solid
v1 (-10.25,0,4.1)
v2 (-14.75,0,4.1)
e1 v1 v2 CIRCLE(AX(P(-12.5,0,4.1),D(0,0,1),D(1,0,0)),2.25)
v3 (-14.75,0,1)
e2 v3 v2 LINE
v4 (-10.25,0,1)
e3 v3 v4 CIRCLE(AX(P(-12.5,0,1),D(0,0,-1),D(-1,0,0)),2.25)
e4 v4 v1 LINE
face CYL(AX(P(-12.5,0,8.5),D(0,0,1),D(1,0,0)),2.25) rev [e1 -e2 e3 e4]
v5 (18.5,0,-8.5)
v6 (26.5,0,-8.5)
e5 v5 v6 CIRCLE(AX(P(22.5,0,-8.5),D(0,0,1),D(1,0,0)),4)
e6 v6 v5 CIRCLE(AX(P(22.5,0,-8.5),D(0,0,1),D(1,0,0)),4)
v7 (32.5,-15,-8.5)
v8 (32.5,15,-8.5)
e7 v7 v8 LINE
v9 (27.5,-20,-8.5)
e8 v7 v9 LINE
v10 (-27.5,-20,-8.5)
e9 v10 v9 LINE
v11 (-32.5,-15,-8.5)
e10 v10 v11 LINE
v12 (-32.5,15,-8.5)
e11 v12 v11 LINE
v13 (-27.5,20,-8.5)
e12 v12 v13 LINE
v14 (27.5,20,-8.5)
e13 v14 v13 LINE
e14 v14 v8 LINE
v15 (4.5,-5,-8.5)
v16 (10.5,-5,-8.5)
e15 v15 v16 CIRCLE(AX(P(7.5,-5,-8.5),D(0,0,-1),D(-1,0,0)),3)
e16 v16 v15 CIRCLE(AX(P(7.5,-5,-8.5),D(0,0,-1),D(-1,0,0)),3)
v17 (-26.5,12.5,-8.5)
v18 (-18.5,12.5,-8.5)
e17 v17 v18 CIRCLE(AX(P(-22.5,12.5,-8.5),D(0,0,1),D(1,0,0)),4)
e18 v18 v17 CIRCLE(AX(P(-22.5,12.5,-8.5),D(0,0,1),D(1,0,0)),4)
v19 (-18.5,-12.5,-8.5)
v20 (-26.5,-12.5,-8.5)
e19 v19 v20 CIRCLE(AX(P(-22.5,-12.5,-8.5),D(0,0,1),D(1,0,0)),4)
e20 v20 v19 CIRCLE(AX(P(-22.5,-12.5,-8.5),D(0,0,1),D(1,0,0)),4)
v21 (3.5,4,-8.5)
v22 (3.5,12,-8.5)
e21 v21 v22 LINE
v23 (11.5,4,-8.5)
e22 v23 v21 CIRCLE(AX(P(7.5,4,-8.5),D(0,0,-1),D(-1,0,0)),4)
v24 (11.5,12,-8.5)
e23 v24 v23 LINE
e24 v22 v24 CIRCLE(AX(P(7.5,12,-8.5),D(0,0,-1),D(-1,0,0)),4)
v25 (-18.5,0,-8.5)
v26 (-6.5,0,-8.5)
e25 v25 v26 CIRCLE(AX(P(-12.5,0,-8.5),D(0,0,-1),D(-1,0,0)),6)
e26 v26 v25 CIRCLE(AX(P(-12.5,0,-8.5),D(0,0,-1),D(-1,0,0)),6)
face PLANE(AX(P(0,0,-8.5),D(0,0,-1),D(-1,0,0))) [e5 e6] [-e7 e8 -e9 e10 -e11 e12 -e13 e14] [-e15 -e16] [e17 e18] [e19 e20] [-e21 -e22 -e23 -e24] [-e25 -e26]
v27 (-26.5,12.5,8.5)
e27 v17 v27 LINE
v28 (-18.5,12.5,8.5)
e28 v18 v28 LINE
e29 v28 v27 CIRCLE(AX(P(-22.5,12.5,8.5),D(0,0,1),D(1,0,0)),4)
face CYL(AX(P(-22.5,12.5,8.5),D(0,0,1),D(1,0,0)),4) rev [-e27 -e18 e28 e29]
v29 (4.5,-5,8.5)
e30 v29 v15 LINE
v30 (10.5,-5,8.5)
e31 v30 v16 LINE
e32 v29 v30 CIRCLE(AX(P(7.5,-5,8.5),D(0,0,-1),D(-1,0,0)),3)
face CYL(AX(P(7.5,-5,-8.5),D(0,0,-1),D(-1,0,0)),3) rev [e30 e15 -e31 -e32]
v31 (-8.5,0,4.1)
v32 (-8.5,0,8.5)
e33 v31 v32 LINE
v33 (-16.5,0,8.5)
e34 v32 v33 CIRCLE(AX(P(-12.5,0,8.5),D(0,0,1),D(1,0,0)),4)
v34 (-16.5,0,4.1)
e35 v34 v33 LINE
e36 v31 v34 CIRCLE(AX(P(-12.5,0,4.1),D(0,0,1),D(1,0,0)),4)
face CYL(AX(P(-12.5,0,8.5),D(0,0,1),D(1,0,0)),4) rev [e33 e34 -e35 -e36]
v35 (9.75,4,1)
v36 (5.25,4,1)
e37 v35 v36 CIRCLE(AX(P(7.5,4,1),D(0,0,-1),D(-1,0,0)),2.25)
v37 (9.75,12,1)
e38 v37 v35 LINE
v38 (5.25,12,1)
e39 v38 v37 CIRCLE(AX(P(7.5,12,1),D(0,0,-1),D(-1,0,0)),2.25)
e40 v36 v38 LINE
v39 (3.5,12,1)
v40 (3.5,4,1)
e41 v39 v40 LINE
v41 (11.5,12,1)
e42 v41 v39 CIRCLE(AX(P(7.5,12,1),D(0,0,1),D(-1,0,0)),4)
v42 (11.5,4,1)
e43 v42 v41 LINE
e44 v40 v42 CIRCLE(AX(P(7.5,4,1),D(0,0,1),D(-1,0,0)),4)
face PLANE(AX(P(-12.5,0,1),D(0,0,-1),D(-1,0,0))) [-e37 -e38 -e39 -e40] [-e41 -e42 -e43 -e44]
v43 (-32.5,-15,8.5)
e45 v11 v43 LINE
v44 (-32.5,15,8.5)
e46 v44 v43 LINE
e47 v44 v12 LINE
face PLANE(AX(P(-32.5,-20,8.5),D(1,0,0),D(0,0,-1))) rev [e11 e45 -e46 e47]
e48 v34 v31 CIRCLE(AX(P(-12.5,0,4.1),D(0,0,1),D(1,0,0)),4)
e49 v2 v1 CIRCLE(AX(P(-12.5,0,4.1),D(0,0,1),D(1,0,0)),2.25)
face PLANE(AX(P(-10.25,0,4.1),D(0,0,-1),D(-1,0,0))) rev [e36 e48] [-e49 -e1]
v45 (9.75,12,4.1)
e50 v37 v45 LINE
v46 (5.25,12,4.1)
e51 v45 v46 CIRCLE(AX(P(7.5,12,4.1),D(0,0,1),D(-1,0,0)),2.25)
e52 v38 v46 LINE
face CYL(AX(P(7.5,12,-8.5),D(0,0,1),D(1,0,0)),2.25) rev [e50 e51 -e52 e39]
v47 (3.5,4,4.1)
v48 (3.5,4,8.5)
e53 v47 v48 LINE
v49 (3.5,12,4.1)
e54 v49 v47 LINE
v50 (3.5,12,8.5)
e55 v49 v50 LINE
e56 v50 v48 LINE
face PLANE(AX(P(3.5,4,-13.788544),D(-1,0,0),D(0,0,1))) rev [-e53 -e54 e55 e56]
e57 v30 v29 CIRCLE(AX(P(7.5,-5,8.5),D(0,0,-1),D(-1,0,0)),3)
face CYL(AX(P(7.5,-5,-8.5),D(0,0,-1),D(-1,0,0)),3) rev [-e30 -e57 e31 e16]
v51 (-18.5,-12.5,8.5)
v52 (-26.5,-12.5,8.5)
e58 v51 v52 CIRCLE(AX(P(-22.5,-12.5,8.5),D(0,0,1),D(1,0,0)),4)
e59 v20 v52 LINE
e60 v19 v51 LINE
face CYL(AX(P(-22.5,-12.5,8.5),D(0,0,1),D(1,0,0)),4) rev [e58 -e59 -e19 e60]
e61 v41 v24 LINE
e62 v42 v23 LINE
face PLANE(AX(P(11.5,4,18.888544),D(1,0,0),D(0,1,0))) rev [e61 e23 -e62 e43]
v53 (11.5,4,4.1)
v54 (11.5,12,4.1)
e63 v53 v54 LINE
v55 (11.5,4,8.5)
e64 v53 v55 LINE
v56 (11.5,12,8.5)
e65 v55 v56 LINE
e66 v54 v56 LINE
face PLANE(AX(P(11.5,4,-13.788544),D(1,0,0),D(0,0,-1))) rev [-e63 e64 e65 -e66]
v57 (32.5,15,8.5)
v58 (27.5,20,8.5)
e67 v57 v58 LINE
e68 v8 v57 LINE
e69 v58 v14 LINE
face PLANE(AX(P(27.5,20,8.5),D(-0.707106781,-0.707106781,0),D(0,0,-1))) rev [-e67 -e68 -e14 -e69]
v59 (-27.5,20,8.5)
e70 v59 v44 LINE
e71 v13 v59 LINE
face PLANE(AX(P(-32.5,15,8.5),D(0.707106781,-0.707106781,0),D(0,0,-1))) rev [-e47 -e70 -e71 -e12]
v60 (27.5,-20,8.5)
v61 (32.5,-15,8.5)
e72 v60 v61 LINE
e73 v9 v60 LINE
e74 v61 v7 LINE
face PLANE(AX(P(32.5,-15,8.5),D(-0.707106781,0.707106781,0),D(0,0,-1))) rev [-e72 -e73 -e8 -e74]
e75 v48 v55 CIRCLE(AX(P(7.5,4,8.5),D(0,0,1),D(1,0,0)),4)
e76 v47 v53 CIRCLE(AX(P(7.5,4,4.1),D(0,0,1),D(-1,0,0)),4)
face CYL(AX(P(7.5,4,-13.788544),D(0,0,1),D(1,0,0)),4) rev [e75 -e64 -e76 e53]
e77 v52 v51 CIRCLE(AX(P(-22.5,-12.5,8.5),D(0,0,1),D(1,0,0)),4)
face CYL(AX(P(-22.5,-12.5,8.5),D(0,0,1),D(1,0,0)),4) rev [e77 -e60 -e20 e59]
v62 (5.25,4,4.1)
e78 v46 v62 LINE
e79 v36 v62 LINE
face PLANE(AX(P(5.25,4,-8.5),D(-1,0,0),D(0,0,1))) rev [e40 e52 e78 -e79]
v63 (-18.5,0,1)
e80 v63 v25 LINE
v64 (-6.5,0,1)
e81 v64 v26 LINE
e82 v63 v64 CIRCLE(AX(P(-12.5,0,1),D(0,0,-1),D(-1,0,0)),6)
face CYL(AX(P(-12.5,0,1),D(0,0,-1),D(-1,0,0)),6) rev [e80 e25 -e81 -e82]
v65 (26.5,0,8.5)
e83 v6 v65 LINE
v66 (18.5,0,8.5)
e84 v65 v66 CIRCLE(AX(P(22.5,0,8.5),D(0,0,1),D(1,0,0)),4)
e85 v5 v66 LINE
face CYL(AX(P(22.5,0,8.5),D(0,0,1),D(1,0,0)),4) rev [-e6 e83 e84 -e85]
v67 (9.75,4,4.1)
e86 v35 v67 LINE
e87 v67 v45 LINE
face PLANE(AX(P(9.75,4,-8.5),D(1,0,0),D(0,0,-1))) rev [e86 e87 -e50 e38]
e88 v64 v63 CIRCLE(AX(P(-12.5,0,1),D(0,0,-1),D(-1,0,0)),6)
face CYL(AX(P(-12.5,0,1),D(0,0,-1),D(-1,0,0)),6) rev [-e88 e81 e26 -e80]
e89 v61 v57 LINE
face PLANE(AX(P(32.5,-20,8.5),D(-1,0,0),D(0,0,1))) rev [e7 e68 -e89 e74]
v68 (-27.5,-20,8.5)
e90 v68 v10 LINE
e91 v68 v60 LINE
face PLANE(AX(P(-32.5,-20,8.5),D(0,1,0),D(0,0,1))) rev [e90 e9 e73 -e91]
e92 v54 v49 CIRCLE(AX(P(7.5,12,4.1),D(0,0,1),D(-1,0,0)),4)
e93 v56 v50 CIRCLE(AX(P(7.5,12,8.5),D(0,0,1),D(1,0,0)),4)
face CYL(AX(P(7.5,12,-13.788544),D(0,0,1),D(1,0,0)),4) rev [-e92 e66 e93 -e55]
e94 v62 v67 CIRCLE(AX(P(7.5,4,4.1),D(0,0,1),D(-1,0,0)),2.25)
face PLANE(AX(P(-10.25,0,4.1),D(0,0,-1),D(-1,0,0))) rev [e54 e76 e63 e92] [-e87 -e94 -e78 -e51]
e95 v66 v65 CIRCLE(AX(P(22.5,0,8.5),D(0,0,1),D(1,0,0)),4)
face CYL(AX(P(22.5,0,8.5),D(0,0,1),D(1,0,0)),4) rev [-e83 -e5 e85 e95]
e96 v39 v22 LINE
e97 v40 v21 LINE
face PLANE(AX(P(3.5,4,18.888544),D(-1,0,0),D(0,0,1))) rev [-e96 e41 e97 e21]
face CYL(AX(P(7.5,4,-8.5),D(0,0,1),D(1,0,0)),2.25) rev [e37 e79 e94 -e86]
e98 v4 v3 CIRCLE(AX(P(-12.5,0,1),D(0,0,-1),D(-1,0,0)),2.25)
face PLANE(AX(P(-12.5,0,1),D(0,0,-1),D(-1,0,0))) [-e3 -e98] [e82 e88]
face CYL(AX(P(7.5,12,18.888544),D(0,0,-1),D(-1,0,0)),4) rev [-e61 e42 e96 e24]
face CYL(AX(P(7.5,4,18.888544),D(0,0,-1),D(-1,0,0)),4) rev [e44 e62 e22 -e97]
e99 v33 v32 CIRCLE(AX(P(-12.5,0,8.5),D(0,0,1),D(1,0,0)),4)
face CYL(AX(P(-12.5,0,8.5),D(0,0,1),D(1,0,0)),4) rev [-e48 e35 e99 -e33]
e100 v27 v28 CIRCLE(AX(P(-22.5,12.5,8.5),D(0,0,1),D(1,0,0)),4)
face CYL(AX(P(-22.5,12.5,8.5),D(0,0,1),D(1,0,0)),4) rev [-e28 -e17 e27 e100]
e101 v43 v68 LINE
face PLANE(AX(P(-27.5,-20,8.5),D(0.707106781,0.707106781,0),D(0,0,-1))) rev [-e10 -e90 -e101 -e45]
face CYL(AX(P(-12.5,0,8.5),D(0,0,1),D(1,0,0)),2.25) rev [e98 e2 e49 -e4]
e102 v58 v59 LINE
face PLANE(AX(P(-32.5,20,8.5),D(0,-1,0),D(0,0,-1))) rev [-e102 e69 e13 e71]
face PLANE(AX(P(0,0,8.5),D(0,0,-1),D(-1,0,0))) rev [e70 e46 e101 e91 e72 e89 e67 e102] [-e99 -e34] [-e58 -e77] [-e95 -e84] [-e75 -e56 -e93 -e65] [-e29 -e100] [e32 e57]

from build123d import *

# Parameters (mm, degrees)
SKETCH_1_W                   = 65
SKETCH_1_H                   = 40
EXTRUDE_1_DEPTH              = 8.5
HOLE_WIZARD_8_0_8_1_D        = 8
SKETCH_4_R                   = 6
CUT_EXTRUDE_1_DEPTH          = 9.5
HOLE_WIZARD_M4_1_D           = 4.5
HOLE_WIZARD_M4_1_CBORE_D     = 8
HOLE_WIZARD_M4_1_CBORE_DEPTH = 4.4
HOLE_WIZARD_6_0_6_1_D        = 6
CUT_EXTRUDE_2_DEPTH          = 9.5
CUT_EXTRUDE_3_DEPTH          = 42.776189391
CUT_EXTRUDE_START            = -4.4
CUT_EXTRUDE_4_DEPTH          = 4.4
CHAMFER_1_SIZE               = 5


with BuildPart() as part:
    # 草图1 → 凸台-拉伸1 (new, symmetric)
    with BuildSketch(Plane.XY):
        Rectangle(SKETCH_1_W, SKETCH_1_H)
    extrude(amount=EXTRUDE_1_DEPTH, both=True)

    # Ø8.0 (8) 直径孔1 (through all)
    with Locations(Plane.XY.offset(8.5)):
        with Locations((-22.5, 12.5), (-22.5, -12.5), (22.5, 0)):
            Hole(HOLE_WIZARD_8_0_8_1_D / 2)

    # 草图4 → 切除-拉伸1 (cut)
    with BuildSketch(Plane(origin=(0, 0, -8.5), x_dir=(-1, 0, 0), z_dir=(0, 0, -1))):
        with Locations((12.5, 0)):
            Circle(SKETCH_4_R)
    extrude(amount=-CUT_EXTRUDE_1_DEPTH, mode=Mode.SUBTRACT)

    # M4 六角凹头螺钉的柱形沉头孔1 (through all)
    with Locations(Plane.XY.offset(8.5)):
        with Locations((-12.5, 0)):
            CounterBoreHole(HOLE_WIZARD_M4_1_D / 2, HOLE_WIZARD_M4_1_CBORE_D / 2, HOLE_WIZARD_M4_1_CBORE_DEPTH)

    # Ø6.0 (6) 直径孔1 (through all)
    with Locations(Plane(origin=(0, 0, -8.5), x_dir=(-1, 0, 0), z_dir=(0, 0, -1))):
        with Locations((-7.5, -5)):
            Hole(HOLE_WIZARD_6_0_6_1_D / 2)

    # 草图9 → 切除-拉伸2 (cut)
    with BuildSketch(Plane(origin=(0, 0, -8.5), x_dir=(-1, 0, 0), z_dir=(0, 0, -1))):
        with BuildLine():
            Line((-11.5, 4), (-11.5, 12))
            ThreePointArc((-11.5, 12), (-7.5, 16), (-3.5, 12))
            Line((-3.5, 12), (-3.5, 4))
            ThreePointArc((-3.5, 4), (-7.5, 0), (-11.5, 4))
        make_face()
    extrude(amount=-CUT_EXTRUDE_2_DEPTH, mode=Mode.SUBTRACT)

    # 草图10 → 切除-拉伸3 (cut, through all)
    with BuildSketch(Plane.XY.offset(8.5)):
        with BuildLine():
            Line((5.25, 4), (5.25, 12))
            ThreePointArc((5.25, 12), (7.5, 14.25), (9.75, 12))
            Line((9.75, 12), (9.75, 4))
            ThreePointArc((9.75, 4), (7.5, 1.75), (5.25, 4))
        make_face()
    extrude(amount=-CUT_EXTRUDE_3_DEPTH, mode=Mode.SUBTRACT)

    # 草图11 → 切除-拉伸4 (cut)
    with BuildSketch(Plane.XY.offset(8.5).offset(CUT_EXTRUDE_START)):
        with BuildLine():
            Line((3.5, 4), (3.5, 12))
            ThreePointArc((3.5, 12), (7.5, 16), (11.5, 12))
            Line((11.5, 12), (11.5, 4))
            ThreePointArc((11.5, 4), (7.5, 0), (3.5, 4))
        make_face()
    extrude(amount=CUT_EXTRUDE_4_DEPTH, mode=Mode.SUBTRACT)

    # 倒角1
    chamfer_1_edges = [part.edges().sort_by_distance(p)[0] for p in [
        (32.5, -20, 0),
        (-32.5, -20, 0),
        (-32.5, 20, 0),
        (32.5, 20, 0),
    ]]
    chamfer(chamfer_1_edges, length=CHAMFER_1_SIZE)


solid = part.part
